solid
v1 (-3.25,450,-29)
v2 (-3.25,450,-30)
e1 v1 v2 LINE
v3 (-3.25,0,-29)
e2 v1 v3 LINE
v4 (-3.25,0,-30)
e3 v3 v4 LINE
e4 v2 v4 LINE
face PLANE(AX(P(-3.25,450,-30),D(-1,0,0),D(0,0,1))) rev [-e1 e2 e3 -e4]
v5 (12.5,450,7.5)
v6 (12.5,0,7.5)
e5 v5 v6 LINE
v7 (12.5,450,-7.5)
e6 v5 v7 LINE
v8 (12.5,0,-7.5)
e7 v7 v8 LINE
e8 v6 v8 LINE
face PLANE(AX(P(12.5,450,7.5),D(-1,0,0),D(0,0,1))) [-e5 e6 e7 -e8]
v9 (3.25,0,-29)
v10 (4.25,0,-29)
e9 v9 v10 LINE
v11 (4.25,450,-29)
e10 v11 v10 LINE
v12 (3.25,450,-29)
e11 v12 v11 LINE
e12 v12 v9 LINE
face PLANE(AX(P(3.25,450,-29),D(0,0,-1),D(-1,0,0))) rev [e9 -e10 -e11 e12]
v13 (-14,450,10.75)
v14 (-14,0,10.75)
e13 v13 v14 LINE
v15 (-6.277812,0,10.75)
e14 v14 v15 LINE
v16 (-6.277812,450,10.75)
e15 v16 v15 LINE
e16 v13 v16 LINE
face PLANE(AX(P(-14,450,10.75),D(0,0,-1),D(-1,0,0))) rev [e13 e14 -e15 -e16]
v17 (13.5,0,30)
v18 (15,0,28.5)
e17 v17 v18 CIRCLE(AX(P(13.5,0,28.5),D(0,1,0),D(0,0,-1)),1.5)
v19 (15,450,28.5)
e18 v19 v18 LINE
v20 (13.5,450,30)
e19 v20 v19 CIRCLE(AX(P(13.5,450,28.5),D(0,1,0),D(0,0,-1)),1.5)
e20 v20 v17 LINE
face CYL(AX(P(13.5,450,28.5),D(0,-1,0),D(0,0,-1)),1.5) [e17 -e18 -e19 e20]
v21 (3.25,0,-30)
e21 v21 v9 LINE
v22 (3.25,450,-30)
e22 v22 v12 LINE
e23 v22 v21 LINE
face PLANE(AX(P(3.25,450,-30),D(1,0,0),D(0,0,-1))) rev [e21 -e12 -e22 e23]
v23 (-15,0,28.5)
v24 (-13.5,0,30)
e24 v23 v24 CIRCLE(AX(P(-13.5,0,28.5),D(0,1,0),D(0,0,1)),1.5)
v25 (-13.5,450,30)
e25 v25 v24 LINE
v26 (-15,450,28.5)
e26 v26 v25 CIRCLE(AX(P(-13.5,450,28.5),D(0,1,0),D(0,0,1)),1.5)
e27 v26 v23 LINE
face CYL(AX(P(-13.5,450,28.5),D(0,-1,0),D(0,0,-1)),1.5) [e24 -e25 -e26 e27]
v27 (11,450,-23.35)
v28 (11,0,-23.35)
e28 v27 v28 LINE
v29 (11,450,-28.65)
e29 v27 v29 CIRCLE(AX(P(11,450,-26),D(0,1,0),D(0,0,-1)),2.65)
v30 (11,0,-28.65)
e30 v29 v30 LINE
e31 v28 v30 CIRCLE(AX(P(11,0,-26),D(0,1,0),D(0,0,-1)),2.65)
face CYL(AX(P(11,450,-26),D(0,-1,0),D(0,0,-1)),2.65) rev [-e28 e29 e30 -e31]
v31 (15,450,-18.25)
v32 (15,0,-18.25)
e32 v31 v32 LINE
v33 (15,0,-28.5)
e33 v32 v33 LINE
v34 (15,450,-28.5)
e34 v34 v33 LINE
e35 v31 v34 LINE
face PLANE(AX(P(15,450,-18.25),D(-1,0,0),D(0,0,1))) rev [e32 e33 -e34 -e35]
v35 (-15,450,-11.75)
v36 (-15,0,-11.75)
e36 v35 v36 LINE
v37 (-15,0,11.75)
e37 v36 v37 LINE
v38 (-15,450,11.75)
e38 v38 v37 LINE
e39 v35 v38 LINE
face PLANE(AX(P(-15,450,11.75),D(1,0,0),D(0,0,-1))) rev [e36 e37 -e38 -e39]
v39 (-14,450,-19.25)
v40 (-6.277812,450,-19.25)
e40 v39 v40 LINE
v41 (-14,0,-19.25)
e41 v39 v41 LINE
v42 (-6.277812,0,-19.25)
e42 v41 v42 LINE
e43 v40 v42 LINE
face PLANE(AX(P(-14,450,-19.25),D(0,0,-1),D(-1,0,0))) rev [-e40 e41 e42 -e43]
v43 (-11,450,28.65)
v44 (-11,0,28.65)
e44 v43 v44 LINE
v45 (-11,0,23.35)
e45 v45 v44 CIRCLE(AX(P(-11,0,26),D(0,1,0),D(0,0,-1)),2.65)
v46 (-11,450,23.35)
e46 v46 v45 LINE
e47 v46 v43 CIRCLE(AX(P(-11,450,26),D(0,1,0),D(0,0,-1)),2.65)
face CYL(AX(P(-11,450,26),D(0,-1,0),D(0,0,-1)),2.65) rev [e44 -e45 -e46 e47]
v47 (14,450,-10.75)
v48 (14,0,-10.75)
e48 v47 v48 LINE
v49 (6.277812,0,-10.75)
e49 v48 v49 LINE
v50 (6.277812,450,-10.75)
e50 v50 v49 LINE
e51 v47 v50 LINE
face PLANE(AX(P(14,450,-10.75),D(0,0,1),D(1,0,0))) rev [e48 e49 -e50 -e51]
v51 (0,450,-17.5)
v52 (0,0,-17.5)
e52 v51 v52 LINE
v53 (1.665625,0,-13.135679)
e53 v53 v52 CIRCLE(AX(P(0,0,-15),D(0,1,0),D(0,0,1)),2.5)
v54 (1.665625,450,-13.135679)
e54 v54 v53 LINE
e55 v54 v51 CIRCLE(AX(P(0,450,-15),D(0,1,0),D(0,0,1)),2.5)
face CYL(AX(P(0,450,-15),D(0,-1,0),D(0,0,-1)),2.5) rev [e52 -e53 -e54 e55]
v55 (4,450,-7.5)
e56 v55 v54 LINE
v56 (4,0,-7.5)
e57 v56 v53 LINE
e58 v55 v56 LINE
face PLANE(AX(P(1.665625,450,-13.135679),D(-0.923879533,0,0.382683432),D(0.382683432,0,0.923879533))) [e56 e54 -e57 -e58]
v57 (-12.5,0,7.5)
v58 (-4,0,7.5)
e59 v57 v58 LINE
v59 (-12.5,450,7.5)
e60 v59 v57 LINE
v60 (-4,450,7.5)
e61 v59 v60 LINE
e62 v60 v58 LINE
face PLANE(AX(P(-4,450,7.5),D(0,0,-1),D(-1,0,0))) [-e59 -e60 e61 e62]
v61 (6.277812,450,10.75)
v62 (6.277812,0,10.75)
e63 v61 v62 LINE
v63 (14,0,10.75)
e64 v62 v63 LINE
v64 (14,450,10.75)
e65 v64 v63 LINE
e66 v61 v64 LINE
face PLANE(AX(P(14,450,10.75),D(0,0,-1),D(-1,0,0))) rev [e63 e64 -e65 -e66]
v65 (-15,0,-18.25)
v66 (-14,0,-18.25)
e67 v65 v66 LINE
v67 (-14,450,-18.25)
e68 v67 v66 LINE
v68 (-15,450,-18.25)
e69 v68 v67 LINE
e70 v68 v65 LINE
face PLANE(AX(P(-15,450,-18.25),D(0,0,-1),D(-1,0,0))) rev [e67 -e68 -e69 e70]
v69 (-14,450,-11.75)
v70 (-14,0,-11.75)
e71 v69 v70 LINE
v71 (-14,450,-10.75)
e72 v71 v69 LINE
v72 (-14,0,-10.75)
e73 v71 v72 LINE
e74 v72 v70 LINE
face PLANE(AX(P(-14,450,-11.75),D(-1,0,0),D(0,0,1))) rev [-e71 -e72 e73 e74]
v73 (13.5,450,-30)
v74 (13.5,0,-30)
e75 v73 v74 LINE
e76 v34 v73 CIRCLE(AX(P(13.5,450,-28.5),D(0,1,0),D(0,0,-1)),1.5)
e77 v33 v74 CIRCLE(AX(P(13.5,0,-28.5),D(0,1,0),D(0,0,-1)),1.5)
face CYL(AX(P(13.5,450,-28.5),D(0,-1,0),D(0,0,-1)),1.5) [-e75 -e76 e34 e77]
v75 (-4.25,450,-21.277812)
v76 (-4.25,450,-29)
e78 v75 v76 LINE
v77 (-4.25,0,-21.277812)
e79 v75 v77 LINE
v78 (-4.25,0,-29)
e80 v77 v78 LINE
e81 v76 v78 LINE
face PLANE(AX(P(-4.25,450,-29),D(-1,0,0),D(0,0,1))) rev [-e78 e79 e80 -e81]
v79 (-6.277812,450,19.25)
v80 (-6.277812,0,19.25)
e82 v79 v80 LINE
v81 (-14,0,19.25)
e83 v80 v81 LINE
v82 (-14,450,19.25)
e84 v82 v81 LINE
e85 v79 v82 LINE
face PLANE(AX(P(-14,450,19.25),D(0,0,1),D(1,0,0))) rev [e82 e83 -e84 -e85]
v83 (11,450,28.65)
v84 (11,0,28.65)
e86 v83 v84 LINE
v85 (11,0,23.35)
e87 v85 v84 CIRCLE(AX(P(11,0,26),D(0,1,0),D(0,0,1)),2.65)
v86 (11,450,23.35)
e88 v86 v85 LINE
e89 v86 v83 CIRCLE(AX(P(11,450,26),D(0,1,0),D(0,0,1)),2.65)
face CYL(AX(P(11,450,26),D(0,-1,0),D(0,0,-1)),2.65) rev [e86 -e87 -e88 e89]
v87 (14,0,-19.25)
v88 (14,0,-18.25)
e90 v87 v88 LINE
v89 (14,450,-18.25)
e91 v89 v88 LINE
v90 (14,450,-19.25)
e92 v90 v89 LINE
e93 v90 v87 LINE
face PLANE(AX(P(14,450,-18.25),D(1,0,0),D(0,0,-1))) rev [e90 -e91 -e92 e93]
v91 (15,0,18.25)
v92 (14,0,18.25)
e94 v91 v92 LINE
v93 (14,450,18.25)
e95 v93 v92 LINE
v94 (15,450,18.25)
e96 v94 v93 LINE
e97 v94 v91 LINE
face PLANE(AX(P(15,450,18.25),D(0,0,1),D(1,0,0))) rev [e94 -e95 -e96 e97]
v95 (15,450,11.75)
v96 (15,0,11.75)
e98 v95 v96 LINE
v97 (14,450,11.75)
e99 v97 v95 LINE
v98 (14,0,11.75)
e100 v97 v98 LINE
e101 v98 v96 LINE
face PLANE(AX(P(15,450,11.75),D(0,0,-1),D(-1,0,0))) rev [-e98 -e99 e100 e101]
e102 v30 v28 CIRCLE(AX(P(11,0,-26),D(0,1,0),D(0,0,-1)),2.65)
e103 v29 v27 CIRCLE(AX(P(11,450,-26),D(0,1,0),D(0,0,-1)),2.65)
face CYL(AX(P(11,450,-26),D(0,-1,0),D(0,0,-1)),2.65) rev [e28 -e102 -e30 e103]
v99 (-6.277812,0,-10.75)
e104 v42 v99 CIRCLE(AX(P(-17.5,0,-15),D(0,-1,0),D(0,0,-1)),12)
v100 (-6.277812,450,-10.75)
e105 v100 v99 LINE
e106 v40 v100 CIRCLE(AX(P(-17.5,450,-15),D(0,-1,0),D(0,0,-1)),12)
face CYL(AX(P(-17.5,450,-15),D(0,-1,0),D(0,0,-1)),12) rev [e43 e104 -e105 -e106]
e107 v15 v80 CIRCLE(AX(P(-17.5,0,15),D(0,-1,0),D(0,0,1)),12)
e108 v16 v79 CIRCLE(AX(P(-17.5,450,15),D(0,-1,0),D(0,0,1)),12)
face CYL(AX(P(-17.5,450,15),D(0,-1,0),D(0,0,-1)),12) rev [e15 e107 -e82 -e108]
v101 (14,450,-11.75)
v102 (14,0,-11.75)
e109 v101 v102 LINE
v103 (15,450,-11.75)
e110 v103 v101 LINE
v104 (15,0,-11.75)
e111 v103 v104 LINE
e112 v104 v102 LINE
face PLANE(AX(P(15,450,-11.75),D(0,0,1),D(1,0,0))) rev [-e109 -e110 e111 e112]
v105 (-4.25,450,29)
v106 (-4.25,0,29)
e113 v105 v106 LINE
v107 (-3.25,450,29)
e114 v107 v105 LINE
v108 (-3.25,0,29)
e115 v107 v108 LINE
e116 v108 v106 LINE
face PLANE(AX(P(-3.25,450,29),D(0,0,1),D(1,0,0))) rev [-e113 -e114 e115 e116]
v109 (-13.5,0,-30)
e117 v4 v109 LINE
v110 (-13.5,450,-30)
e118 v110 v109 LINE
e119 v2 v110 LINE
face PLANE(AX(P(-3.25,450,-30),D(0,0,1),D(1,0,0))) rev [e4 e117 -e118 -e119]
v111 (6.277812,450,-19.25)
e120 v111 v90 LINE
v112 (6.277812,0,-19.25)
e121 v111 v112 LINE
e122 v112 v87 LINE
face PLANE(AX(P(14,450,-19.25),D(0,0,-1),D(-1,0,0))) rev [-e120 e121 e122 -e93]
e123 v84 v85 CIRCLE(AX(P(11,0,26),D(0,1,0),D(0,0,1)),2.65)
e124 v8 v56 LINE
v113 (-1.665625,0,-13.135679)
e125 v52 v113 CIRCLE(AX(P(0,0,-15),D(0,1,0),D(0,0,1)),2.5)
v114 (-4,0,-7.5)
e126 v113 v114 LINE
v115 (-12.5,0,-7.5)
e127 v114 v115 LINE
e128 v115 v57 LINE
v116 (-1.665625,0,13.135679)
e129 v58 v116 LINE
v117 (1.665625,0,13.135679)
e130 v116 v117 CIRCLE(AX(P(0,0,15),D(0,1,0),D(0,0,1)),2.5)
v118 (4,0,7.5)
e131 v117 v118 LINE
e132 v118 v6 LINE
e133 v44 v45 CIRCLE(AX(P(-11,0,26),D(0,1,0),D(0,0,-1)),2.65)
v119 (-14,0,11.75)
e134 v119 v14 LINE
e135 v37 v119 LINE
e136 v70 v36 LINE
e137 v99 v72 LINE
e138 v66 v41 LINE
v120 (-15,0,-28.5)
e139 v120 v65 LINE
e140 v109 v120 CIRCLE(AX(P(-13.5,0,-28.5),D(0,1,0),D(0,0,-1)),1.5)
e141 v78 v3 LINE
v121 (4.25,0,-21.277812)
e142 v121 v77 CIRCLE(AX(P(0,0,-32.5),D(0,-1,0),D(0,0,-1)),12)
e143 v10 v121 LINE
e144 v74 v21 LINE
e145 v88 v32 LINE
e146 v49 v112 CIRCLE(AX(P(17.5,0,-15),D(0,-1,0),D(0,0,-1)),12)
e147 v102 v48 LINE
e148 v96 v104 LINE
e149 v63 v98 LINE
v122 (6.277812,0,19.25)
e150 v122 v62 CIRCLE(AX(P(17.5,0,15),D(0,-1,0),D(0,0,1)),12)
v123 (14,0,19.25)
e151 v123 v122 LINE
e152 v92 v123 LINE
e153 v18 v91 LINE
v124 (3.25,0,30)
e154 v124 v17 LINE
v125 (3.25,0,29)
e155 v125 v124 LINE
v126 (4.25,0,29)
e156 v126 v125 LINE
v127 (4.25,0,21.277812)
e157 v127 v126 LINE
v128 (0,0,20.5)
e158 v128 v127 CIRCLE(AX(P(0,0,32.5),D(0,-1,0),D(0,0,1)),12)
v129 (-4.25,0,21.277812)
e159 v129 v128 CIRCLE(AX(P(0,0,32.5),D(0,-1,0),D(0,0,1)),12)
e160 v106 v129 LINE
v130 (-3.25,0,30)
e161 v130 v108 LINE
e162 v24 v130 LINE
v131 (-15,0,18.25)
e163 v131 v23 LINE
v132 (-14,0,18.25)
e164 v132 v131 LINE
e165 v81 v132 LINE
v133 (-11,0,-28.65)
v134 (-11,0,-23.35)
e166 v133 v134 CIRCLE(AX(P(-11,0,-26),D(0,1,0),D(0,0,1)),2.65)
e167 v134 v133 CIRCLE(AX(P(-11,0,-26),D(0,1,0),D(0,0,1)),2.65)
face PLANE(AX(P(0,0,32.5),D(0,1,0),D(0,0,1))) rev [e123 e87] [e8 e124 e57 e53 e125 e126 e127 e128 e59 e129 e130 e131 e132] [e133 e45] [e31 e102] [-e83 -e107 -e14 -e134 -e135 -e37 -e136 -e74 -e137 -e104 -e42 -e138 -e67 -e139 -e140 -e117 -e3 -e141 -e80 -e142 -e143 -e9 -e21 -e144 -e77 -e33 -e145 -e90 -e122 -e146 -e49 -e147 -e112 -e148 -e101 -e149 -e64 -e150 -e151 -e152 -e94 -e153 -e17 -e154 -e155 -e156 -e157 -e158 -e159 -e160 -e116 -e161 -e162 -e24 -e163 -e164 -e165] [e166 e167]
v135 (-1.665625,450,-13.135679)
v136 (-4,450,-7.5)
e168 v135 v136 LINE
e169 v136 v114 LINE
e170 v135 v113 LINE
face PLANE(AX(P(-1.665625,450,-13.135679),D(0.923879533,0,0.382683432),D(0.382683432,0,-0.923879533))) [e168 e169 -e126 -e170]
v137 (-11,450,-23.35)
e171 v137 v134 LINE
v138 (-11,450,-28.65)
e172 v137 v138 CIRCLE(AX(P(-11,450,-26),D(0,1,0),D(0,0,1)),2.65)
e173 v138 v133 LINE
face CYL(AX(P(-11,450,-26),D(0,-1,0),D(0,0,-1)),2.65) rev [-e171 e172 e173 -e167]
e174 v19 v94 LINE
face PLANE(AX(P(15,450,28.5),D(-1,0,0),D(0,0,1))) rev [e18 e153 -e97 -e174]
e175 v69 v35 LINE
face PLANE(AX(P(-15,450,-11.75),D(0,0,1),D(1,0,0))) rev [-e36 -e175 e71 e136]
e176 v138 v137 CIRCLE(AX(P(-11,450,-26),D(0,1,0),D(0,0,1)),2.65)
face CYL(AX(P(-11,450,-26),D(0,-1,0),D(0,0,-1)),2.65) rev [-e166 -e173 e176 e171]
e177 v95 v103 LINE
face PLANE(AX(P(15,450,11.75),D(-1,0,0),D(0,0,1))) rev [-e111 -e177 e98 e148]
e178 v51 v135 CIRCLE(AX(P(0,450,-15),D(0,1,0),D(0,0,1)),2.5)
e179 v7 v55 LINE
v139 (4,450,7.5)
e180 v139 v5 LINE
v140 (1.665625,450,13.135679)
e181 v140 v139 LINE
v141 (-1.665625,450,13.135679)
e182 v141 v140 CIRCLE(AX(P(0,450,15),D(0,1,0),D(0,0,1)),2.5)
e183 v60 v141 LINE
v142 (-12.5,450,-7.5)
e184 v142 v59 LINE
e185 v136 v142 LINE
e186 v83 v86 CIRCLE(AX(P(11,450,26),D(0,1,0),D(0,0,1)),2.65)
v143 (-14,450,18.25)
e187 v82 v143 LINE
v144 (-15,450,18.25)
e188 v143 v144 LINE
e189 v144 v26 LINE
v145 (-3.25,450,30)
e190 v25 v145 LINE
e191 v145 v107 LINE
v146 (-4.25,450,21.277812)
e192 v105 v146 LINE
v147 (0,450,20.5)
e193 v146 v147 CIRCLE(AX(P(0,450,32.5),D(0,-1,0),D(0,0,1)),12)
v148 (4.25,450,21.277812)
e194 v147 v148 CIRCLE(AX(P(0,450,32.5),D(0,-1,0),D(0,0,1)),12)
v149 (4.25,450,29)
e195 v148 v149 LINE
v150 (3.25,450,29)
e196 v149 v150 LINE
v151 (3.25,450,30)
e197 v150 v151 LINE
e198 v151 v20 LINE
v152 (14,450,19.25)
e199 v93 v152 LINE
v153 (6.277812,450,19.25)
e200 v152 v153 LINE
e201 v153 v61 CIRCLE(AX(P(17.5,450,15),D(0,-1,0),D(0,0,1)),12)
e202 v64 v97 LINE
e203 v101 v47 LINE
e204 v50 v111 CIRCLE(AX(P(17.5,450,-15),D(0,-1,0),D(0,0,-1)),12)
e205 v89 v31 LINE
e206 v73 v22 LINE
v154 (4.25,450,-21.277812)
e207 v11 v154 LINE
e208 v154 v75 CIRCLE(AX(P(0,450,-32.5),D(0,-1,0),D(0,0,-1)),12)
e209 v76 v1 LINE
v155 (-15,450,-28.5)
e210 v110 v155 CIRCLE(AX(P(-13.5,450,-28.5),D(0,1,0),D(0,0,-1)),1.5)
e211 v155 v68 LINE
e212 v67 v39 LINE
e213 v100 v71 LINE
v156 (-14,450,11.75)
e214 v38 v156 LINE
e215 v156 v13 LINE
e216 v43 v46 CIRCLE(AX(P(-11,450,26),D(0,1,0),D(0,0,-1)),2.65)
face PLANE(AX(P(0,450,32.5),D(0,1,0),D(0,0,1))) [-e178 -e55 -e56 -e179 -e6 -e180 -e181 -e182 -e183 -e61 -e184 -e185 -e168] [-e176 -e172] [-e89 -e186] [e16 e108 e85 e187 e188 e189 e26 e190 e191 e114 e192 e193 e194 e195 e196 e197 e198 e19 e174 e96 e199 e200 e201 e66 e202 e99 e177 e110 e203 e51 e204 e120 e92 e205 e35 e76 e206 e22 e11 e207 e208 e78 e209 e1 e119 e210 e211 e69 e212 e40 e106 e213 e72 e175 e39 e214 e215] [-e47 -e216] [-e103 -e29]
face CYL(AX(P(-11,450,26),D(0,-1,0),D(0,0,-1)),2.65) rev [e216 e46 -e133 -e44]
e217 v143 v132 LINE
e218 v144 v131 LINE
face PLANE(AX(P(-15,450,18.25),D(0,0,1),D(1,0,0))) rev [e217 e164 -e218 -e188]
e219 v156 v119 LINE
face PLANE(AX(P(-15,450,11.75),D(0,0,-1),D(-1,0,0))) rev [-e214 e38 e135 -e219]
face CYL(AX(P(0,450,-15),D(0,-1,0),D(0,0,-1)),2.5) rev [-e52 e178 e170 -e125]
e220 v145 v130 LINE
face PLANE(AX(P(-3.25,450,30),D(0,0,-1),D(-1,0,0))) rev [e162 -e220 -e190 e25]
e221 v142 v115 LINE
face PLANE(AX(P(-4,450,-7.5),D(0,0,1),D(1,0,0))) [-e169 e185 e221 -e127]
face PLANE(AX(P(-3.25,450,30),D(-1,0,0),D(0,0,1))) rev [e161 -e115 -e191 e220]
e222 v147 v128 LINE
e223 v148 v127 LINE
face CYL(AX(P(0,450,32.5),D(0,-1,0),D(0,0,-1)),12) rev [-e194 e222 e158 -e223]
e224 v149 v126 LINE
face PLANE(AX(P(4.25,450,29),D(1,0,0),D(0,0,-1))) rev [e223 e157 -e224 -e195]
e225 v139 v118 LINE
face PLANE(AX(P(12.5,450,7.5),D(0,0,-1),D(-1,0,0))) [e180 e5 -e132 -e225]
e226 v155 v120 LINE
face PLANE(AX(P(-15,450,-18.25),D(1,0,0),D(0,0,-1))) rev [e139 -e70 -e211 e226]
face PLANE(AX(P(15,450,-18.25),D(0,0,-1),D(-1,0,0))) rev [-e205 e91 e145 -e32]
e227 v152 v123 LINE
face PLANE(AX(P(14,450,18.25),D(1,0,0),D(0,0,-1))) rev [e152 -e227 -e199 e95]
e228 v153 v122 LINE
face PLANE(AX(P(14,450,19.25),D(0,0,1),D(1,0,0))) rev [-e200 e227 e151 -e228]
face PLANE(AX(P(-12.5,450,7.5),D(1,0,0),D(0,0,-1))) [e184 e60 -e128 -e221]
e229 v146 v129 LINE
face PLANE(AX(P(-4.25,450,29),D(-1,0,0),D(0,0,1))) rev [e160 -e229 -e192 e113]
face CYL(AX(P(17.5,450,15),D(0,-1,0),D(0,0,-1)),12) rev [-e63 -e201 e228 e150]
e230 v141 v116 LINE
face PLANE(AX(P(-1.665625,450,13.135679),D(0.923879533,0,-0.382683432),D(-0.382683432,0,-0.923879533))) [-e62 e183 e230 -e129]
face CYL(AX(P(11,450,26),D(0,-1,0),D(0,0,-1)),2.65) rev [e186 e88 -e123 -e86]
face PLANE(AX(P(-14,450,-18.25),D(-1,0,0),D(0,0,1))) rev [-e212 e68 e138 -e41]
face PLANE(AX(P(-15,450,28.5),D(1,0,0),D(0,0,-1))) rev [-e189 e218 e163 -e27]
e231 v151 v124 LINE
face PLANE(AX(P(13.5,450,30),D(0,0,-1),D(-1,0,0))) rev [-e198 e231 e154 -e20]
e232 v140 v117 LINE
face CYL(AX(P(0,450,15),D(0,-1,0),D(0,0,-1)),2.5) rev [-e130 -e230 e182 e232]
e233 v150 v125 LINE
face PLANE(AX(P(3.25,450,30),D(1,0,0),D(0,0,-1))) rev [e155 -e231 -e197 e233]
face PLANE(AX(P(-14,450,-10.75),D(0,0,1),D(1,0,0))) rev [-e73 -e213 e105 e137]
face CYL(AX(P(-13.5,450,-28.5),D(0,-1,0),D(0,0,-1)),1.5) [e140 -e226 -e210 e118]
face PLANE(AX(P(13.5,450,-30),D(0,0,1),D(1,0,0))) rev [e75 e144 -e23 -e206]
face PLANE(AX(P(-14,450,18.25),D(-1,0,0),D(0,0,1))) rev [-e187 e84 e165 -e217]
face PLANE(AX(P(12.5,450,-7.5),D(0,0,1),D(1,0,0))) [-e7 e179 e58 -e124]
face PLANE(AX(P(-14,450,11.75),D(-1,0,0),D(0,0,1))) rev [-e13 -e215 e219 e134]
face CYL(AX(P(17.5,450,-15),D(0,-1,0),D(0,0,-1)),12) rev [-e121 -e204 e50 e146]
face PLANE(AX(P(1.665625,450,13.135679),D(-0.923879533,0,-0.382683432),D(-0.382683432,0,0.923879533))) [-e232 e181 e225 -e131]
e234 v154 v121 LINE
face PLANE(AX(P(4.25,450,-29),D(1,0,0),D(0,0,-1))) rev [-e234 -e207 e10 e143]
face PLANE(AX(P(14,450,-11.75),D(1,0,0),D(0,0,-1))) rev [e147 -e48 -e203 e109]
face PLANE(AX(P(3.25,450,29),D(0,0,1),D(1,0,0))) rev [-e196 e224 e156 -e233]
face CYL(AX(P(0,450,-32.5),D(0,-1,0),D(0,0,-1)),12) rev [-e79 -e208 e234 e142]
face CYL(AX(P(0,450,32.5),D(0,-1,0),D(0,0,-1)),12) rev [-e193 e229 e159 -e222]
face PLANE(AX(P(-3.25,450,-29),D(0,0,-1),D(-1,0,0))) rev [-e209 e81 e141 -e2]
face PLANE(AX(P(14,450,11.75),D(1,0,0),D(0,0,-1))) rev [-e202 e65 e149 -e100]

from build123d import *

# Parameters (mm, degrees)
SKETCH1_R                 = 2.65
F_30_X_60G_X_R1_5_1_DEPTH = 450


with BuildPart() as part:
    # Sketch1 → 工业铝型材 30 X 60G X R1.5(1) (new body)
    with BuildSketch(Plane(origin=(0, 0, 0), x_dir=(-1, 0, 0), z_dir=(0, 1, 0))):
        with BuildLine():
            Line((-3.25, 30), (-3.25, 29))
            Line((-3.25, 29), (-4.25, 29))
            Line((-4.25, 29), (-4.25, 21.277812156))
            ThreePointArc((-4.25, 21.277812156), (0, 20.5), (4.25, 21.277812156))
            Line((4.25, 21.277812156), (4.25, 29))
            Line((4.25, 29), (3.25, 29))
            Line((3.25, 29), (3.25, 30))
            Line((3.25, 30), (13.5, 30))
            ThreePointArc((13.5, 30), (14.560660172, 29.560660172), (15, 28.5))
            Line((15, 28.5), (15, 18.25))
            Line((15, 18.25), (14, 18.25))
            Line((14, 18.25), (14, 19.25))
            Line((14, 19.25), (6.277812156, 19.25))
            ThreePointArc((6.277812156, 19.25), (5.5, 15), (6.277812156, 10.75))
            Line((6.277812156, 10.75), (14, 10.75))
            Line((14, 10.75), (14, 11.75))
            Line((14, 11.75), (15, 11.75))
            Line((15, 11.75), (15, -11.75))
            Line((15, -11.75), (14, -11.75))
            Line((14, -11.75), (14, -10.75))
            Line((14, -10.75), (6.277812156, -10.75))
            ThreePointArc((6.277812156, -10.75), (5.5, -15), (6.277812156, -19.25))
            Line((6.277812156, -19.25), (14, -19.25))
            Line((14, -19.25), (14, -18.25))
            Line((14, -18.25), (15, -18.25))
            Line((15, -18.25), (15, -28.5))
            ThreePointArc((15, -28.5), (14.560660172, -29.560660172), (13.5, -30))
            Line((13.5, -30), (3.25, -30))
            Line((3.25, -30), (3.25, -29))
            Line((3.25, -29), (4.25, -29))
            Line((4.25, -29), (4.25, -21.277812156))
            ThreePointArc((4.25, -21.277812156), (0, -20.5), (-4.25, -21.277812156))
            Line((-4.25, -21.277812156), (-4.25, -29))
            Line((-4.25, -29), (-3.25, -29))
            Line((-3.25, -29), (-3.25, -30))
            Line((-3.25, -30), (-13.5, -30))
            ThreePointArc((-13.5, -30), (-14.560660172, -29.560660172), (-15, -28.5))
            Line((-15, -28.5), (-15, -18.25))
            Line((-15, -18.25), (-14, -18.25))
            Line((-14, -18.25), (-14, -19.25))
            Line((-14, -19.25), (-6.277812156, -19.25))
            ThreePointArc((-6.277812156, -19.25), (-5.5, -15), (-6.277812156, -10.75))
            Line((-6.277812156, -10.75), (-14, -10.75))
            Line((-14, -10.75), (-14, -11.75))
            Line((-14, -11.75), (-15, -11.75))
            Line((-15, -11.75), (-15, 11.75))
            Line((-15, 11.75), (-14, 11.75))
            Line((-14, 11.75), (-14, 10.75))
            Line((-14, 10.75), (-6.277812156, 10.75))
            ThreePointArc((-6.277812156, 10.75), (-5.5, 15), (-6.277812156, 19.25))
            Line((-6.277812156, 19.25), (-14, 19.25))
            Line((-14, 19.25), (-14, 18.25))
            Line((-14, 18.25), (-15, 18.25))
            Line((-15, 18.25), (-15, 28.5))
            ThreePointArc((-15, 28.5), (-14.560660172, 29.560660172), (-13.5, 30))
            Line((-13.5, 30), (-3.25, 30))
        make_face()
        with Locations((-11, 26)):
            Circle(SKETCH1_R, mode=Mode.SUBTRACT)
        with Locations((11, 26)):
            Circle(SKETCH1_R, mode=Mode.SUBTRACT)
        with Locations((11, -26)):
            Circle(SKETCH1_R, mode=Mode.SUBTRACT)
        with Locations((-11, -26)):
            Circle(SKETCH1_R, mode=Mode.SUBTRACT)
        with BuildLine():
            Line((-12.5, 7.5), (-4, 7.5))
            Line((-4, 7.5), (-1.665625283, 13.135679101))
            ThreePointArc((-1.665625283, 13.135679101), (0, 17.5), (1.665625283, 13.135679101))
            Line((1.665625283, 13.135679101), (4, 7.5))
            Line((4, 7.5), (12.5, 7.5))
            Line((12.5, 7.5), (12.5, -7.5))
            Line((12.5, -7.5), (4, -7.5))
            Line((4, -7.5), (1.665625283, -13.135679101))
            ThreePointArc((1.665625283, -13.135679101), (0, -17.5), (-1.665625283, -13.135679101))
            Line((-1.665625283, -13.135679101), (-4, -7.5))
            Line((-4, -7.5), (-12.5, -7.5))
            Line((-12.5, -7.5), (-12.5, 7.5))
        make_face(mode=Mode.SUBTRACT)
    extrude(amount=F_30_X_60G_X_R1_5_1_DEPTH)


solid = part.part
